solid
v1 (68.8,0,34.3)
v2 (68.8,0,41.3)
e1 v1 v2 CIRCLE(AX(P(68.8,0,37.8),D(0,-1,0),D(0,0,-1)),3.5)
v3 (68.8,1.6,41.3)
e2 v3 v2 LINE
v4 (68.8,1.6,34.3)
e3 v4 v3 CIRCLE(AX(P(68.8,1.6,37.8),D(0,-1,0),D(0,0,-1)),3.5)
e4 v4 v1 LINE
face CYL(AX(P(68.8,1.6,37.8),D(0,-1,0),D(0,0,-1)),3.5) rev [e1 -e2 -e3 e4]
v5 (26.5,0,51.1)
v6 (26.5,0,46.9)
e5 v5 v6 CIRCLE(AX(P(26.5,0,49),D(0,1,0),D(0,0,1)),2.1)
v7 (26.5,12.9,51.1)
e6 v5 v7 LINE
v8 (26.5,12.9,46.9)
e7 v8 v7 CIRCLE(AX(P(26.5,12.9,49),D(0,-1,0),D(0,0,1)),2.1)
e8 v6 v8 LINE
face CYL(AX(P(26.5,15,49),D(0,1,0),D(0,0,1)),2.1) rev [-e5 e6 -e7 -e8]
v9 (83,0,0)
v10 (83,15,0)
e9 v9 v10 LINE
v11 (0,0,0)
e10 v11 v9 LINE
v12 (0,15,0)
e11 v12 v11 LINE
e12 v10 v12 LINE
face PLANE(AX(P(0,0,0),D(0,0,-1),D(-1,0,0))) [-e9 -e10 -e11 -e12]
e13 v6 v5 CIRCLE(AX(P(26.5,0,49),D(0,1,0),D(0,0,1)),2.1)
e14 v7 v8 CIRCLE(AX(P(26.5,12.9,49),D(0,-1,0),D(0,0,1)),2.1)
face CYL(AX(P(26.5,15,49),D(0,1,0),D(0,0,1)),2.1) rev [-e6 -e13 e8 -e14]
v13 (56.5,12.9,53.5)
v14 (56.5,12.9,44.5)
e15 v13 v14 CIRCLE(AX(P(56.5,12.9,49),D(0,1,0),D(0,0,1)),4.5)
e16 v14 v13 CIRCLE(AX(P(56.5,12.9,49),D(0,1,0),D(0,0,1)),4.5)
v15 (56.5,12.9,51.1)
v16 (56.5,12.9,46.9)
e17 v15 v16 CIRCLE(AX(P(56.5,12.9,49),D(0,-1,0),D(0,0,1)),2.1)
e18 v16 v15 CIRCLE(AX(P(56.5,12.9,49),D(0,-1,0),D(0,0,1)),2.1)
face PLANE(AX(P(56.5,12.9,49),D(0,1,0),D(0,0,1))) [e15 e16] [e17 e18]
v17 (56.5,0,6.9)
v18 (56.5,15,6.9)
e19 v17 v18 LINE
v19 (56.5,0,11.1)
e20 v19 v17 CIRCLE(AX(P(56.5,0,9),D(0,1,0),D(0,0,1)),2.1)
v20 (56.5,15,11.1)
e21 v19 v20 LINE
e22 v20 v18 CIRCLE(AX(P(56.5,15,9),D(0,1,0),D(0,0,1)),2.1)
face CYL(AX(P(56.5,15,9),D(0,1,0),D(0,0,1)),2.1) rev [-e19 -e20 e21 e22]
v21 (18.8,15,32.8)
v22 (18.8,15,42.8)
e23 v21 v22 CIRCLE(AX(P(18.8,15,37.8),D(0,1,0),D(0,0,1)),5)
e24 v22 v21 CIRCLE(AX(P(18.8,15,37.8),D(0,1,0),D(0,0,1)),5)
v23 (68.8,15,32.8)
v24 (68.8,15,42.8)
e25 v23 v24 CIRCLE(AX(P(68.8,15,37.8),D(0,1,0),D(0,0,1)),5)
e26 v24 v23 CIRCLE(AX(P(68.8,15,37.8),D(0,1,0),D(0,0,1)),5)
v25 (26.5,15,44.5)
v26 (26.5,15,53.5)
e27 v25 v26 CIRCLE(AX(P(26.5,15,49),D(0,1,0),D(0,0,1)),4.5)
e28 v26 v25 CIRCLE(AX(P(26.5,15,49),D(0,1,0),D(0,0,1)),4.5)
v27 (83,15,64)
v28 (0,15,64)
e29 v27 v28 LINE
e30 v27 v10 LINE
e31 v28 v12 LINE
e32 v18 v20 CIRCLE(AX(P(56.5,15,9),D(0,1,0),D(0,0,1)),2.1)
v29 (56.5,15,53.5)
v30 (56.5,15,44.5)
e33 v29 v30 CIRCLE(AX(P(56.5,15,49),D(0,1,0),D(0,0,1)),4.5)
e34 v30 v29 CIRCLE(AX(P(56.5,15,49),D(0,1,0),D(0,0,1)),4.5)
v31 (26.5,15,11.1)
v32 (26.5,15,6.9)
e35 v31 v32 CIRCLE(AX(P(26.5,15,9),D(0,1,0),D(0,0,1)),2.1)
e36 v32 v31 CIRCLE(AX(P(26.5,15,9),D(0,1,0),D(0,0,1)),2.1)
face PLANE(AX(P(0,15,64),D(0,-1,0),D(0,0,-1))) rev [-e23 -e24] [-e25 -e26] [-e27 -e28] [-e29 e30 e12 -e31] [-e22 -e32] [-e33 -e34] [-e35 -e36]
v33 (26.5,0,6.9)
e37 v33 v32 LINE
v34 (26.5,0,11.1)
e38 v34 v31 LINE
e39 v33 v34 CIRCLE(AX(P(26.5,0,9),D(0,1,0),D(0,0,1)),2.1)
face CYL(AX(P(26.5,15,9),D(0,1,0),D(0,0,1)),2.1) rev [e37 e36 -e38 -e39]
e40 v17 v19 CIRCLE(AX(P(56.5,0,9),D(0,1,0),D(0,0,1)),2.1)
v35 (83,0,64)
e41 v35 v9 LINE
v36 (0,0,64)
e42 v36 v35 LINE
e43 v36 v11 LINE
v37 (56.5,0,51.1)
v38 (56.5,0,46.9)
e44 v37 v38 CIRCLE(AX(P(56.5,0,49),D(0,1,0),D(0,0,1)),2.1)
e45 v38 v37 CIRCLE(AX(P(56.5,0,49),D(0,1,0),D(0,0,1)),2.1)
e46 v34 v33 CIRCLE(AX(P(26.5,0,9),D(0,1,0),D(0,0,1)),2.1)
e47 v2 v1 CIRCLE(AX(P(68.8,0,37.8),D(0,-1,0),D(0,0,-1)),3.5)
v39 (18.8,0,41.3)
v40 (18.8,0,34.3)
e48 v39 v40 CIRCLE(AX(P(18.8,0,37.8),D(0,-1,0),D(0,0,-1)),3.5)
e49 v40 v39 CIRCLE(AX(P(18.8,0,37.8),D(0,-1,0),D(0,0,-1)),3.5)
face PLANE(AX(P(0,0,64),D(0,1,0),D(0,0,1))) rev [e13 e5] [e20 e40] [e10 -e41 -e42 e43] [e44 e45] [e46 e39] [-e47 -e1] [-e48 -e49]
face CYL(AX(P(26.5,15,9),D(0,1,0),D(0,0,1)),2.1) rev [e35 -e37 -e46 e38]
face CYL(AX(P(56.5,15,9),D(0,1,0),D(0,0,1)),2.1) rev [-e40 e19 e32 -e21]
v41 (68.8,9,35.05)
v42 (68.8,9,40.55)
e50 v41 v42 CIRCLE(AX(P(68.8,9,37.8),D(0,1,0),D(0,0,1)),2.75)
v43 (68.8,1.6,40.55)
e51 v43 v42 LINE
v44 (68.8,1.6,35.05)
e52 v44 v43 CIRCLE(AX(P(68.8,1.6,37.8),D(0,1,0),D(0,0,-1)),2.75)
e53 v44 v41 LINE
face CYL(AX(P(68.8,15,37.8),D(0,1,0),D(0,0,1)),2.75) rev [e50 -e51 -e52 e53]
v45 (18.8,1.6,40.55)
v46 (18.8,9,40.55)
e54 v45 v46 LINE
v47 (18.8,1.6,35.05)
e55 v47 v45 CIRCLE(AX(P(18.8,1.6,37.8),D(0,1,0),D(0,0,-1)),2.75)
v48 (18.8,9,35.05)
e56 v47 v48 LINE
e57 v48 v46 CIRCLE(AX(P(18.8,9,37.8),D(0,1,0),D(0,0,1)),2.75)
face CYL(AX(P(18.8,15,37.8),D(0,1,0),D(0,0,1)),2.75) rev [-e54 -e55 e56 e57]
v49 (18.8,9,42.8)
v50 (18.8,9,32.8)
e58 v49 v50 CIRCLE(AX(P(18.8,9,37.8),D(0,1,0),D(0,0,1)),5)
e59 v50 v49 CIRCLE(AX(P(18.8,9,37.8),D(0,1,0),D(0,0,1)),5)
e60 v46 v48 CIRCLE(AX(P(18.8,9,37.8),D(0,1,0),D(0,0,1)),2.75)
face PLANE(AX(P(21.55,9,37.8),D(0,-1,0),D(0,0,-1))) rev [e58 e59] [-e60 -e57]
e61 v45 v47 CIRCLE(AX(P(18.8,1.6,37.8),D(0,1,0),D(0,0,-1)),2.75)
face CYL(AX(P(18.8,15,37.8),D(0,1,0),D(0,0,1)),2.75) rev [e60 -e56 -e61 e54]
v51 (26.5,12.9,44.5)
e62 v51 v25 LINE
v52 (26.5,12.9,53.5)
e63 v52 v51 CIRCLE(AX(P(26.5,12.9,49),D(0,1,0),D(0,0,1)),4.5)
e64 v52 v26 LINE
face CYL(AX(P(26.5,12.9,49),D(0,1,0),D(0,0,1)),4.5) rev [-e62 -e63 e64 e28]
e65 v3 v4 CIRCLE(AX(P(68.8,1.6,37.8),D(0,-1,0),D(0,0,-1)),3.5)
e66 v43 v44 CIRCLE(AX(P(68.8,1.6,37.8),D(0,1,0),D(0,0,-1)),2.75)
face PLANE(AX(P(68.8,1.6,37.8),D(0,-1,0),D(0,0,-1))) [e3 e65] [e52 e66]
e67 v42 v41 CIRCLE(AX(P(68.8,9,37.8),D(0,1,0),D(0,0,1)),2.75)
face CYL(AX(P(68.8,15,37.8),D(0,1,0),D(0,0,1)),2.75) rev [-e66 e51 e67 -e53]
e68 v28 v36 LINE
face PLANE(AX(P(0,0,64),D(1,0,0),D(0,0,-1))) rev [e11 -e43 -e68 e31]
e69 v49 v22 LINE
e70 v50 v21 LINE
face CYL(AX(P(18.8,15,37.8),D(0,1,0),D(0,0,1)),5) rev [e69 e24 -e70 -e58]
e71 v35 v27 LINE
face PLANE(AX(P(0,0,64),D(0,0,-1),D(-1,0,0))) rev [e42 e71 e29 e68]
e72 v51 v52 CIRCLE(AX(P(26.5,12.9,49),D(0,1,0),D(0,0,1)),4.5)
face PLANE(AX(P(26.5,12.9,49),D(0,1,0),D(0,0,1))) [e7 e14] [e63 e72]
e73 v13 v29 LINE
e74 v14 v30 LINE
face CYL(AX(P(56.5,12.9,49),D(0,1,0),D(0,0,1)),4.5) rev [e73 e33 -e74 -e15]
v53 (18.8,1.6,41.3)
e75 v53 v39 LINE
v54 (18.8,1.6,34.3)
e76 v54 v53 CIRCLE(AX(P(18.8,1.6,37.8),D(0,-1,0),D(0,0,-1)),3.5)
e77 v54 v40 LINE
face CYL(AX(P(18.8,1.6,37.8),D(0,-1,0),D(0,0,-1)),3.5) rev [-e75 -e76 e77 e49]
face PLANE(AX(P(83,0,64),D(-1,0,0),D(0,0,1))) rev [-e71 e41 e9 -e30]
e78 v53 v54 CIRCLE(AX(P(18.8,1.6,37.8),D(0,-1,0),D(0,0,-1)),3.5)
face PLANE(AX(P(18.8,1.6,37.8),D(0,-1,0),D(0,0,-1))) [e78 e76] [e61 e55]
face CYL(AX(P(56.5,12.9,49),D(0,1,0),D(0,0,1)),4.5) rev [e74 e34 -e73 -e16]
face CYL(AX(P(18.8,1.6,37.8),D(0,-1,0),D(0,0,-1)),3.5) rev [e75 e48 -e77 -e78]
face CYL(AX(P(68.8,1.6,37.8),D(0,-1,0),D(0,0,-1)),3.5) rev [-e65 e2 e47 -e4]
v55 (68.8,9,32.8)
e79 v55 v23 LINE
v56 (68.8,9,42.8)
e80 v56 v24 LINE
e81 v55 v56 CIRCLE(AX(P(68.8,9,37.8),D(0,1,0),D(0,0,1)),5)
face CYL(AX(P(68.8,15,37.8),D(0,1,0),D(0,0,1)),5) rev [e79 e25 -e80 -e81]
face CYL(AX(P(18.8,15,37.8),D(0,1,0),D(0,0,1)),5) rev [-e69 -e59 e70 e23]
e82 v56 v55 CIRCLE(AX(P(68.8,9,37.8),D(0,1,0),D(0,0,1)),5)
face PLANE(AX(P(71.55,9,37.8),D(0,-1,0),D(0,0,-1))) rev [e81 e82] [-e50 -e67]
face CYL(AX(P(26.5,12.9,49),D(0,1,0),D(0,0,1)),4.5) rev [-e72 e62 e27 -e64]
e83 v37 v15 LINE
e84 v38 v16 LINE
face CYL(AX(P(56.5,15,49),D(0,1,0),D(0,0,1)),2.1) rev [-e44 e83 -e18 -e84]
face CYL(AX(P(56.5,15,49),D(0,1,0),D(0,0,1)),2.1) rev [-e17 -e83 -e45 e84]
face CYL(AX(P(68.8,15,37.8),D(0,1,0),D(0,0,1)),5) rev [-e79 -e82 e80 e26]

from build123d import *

# Parameters (mm, degrees)
SKETCH1_W                                            = 83
SKETCH1_H                                            = 15
BOSS_EXTRUDE1_DEPTH                                  = 64
HOLE_SIZE_PER_SOCKET_HEAD_CAP_SCREW_TYPE_D           = 5.5
HOLE_SIZE_PER_SOCKET_HEAD_CAP_SCREW_TYPE_CBORE_D     = 10
HOLE_SIZE_PER_SOCKET_HEAD_CAP_SCREW_TYPE_CBORE_DEPTH = 6
SKETCH5_R                                            = 3.5
CUT_EXTRUDE1_DEPTH                                   = 1.6
M5_TAPPED_HOLE1_D                                    = 4.2
SKETCH8_R                                            = 4.5
CUT_EXTRUDE2_DEPTH                                   = 2.1


with BuildPart() as part:
    # Sketch1 → Boss-Extrude1 (new body)
    with BuildSketch(Plane.XY):
        with Locations((41.5, 7.5)):
            Rectangle(SKETCH1_W, SKETCH1_H)
    extrude(amount=BOSS_EXTRUDE1_DEPTH)

    # Hole size per socket head cap screw type 1 (through all)
    with Locations(Plane(origin=(0, 15, 0), x_dir=(1, 0, 0), z_dir=(0, 1, 0))):
        with Locations((18.8, -37.8), (68.8, -37.8)):
            CounterBoreHole(HOLE_SIZE_PER_SOCKET_HEAD_CAP_SCREW_TYPE_D / 2, HOLE_SIZE_PER_SOCKET_HEAD_CAP_SCREW_TYPE_CBORE_D / 2, HOLE_SIZE_PER_SOCKET_HEAD_CAP_SCREW_TYPE_CBORE_DEPTH)

    # Sketch5 → Cut-Extrude1 (cut)
    with BuildSketch(Plane.XZ):
        with Locations(Location((18.8, 37.8, 0), (0, 0, 270))):
            Circle(SKETCH5_R)
        with Locations(Location((68.8, 37.8, 0), (0, 0, 270))):
            Circle(SKETCH5_R)
    extrude(amount=-CUT_EXTRUDE1_DEPTH, mode=Mode.SUBTRACT)

    # M5 Tapped Hole1 (through all)
    with Locations(Plane(origin=(0, 15, 0), x_dir=(1, 0, 0), z_dir=(0, 1, 0))):
        with Locations((56.5, -9), (26.5, -9), (26.5, -49), (56.5, -49)):
            Hole(M5_TAPPED_HOLE1_D / 2)

    # Sketch8 → Cut-Extrude2 (cut)
    with BuildSketch(Plane(origin=(0, 15, 0), x_dir=(1, 0, 0), z_dir=(0, 1, 0))):
        with Locations(Location((26.5, -49, 0), (0, 0, 270))):
            Circle(SKETCH8_R)
        with Locations(Location((56.5, -49, 0), (0, 0, 270))):
            Circle(SKETCH8_R)
    extrude(amount=-CUT_EXTRUDE2_DEPTH, mode=Mode.SUBTRACT)


solid = part.part
